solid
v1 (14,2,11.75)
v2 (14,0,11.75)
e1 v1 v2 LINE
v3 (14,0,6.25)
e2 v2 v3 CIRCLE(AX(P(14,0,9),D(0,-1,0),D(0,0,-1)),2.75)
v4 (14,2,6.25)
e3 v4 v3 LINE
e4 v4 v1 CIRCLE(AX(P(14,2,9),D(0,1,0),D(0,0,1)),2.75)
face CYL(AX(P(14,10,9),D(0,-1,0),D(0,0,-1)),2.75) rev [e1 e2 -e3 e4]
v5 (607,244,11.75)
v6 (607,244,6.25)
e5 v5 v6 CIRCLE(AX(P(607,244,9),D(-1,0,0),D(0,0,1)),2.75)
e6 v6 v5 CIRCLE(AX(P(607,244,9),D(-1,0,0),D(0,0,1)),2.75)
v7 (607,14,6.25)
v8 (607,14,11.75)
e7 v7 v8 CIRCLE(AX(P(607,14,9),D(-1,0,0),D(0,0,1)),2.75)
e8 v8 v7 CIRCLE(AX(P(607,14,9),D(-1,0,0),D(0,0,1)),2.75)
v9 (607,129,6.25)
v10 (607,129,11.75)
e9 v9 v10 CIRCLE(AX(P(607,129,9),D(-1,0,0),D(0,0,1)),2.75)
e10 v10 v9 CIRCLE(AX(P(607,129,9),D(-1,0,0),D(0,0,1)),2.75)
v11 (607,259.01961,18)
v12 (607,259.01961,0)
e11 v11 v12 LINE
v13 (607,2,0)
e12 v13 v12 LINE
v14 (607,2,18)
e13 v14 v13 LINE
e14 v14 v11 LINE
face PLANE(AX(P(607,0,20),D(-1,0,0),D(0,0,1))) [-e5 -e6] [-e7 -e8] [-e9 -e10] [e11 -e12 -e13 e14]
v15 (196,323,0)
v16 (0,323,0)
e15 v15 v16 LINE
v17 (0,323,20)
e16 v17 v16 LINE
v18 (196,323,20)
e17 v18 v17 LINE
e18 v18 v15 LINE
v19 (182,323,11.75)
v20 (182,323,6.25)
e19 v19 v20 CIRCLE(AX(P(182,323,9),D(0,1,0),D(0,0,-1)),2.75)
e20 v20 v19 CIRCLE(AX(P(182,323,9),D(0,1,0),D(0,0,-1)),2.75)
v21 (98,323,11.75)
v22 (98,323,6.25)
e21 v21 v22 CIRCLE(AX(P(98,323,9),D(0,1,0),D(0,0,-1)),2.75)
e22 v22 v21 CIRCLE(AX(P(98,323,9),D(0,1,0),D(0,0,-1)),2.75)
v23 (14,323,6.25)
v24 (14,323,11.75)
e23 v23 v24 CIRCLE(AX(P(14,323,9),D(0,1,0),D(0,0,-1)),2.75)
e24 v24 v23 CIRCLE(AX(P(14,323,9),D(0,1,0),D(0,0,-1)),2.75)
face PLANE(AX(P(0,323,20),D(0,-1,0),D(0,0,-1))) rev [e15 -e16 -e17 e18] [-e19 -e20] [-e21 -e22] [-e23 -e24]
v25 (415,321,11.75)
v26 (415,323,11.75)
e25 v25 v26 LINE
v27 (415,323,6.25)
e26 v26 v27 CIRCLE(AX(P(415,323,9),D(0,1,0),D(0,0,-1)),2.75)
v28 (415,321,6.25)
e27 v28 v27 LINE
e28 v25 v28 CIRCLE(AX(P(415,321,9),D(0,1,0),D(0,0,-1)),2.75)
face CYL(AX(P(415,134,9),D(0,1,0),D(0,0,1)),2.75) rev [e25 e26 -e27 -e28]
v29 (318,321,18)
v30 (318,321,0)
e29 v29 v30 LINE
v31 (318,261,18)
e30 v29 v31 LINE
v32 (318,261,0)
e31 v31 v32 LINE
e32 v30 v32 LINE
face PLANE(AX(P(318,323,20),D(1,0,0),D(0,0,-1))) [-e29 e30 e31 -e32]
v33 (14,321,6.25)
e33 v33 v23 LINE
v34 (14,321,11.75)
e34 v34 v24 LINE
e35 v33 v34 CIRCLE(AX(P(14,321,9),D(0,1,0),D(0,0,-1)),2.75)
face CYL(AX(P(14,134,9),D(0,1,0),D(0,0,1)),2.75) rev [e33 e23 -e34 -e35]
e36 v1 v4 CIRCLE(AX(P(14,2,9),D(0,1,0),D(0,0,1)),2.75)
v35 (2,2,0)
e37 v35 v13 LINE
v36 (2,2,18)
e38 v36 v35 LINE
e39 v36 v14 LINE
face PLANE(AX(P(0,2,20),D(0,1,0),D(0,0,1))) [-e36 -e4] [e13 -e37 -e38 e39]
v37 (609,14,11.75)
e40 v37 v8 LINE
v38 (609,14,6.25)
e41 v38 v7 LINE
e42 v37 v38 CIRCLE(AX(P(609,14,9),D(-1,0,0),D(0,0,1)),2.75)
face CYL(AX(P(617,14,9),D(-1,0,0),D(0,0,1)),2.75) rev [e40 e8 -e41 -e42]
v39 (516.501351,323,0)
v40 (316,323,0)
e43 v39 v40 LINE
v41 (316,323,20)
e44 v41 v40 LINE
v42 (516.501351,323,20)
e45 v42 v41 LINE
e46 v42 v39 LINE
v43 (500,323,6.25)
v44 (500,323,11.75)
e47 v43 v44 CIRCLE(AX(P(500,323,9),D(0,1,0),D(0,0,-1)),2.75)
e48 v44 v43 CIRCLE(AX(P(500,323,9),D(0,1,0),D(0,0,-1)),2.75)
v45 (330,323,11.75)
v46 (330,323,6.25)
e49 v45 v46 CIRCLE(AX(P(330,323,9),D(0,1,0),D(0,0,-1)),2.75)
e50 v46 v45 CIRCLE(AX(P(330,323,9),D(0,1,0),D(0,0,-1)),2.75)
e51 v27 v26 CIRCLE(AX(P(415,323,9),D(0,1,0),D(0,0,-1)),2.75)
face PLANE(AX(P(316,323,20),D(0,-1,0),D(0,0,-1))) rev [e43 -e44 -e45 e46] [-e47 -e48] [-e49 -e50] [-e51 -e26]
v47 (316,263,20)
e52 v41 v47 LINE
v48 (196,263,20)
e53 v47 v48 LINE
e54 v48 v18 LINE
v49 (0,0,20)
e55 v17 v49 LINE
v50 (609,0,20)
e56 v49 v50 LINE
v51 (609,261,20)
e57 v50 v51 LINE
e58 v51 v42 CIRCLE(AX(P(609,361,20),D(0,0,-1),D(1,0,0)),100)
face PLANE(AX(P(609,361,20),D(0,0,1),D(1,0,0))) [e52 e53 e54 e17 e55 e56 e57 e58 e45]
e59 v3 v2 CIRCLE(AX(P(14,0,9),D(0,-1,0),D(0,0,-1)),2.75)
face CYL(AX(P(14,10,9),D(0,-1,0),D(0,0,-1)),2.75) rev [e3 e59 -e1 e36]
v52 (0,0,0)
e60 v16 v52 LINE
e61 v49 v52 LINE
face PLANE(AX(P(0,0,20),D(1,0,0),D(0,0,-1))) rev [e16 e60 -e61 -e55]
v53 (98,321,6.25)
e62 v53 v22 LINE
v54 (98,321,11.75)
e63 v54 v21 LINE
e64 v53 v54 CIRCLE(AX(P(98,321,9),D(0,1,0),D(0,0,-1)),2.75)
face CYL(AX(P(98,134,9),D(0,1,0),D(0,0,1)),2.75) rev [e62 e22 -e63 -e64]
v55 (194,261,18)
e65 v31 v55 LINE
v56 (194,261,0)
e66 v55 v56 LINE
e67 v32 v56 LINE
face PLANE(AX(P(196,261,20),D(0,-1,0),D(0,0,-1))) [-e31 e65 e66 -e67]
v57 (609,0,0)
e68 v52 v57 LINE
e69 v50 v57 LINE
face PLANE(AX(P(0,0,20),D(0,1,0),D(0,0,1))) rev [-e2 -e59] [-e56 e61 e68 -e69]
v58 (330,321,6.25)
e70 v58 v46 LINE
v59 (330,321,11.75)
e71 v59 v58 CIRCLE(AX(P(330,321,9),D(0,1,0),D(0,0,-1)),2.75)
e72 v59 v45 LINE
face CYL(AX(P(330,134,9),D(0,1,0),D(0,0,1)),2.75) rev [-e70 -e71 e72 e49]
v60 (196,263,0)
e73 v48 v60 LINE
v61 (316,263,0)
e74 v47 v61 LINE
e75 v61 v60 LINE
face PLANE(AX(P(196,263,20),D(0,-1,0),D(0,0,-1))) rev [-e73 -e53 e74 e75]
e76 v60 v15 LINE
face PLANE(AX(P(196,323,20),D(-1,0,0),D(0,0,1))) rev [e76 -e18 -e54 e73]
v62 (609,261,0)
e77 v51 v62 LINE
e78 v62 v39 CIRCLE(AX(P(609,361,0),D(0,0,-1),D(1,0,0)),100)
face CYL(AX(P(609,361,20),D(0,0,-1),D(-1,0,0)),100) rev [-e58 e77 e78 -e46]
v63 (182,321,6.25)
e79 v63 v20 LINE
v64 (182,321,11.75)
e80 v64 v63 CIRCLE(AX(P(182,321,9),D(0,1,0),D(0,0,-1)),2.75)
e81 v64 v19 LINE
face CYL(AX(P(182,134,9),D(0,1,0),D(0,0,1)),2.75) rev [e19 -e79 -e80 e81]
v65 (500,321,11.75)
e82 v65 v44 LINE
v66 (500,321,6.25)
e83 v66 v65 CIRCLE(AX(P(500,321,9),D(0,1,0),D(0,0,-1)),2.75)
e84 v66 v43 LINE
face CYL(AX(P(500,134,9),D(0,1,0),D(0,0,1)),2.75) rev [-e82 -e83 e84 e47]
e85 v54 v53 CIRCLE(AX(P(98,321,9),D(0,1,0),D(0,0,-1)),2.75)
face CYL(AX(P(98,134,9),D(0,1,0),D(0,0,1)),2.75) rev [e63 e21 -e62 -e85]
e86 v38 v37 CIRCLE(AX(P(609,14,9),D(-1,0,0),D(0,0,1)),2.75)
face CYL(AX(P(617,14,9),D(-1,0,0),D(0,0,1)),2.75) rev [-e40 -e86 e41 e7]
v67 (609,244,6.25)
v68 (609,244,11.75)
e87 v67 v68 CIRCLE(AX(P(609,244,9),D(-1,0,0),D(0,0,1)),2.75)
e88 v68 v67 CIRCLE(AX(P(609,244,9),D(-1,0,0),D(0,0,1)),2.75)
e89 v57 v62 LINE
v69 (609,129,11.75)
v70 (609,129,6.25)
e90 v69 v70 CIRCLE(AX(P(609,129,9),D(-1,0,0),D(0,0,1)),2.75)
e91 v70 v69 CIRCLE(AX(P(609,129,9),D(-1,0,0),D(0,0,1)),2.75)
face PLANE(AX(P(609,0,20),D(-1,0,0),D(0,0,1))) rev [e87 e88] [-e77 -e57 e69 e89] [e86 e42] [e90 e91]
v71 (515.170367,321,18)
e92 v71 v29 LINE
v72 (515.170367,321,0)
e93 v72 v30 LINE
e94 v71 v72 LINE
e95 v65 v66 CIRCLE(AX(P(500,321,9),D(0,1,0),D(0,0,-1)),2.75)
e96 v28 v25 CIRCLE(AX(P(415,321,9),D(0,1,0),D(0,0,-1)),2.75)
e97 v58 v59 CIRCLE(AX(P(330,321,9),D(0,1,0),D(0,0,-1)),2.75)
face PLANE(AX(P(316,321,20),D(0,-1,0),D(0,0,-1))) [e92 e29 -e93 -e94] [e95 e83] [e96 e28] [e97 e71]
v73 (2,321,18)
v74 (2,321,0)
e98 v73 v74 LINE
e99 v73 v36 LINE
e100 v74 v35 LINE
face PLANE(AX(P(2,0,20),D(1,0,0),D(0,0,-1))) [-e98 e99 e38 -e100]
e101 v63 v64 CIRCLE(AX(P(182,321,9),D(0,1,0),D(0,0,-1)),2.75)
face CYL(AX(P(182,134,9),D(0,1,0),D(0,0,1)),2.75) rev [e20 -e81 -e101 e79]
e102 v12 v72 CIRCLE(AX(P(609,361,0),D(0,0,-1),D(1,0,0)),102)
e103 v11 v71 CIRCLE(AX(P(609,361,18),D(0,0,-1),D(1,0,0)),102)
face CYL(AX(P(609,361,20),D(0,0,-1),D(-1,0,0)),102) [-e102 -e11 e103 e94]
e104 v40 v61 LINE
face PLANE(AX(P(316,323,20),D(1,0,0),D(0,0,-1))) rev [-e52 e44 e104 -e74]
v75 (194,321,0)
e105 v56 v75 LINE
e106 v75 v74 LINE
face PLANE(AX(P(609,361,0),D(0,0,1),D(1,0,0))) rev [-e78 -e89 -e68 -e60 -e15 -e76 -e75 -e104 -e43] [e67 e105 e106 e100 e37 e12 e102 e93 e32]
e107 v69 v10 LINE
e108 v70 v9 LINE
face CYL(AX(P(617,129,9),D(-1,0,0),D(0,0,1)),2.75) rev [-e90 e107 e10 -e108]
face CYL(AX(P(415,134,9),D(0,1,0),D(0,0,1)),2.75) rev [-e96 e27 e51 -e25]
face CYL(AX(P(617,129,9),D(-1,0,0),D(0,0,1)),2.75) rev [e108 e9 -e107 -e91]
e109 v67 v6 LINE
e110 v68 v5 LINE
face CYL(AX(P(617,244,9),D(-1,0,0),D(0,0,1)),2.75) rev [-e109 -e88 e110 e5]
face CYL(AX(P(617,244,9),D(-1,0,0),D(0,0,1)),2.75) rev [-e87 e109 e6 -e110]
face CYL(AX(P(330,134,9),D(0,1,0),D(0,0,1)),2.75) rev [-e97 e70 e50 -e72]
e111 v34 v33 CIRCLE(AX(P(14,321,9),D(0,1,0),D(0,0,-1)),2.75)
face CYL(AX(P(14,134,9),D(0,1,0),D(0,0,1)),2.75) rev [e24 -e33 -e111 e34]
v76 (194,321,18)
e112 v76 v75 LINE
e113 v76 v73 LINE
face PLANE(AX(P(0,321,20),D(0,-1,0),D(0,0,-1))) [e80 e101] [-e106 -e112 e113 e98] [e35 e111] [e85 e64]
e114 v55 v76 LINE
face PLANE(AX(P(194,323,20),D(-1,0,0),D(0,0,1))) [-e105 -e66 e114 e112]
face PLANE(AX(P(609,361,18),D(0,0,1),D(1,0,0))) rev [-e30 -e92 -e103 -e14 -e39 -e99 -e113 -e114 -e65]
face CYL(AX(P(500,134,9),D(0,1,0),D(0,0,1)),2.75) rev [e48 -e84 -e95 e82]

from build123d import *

# Parameters (mm, degrees)
EXTRUDE_1_DEPTH          = 20
SHELL_1_T                = -2
CUT_EXTRUDE_1_DEPTH      = 187
CUT_EXTRUDE_1_DEPTH_BACK = 10
SKETCH_2_R               = 2.75
SKETCH_3_R               = 2.75
CUT_EXTRUDE_2_DEPTH      = 10
SKETCH_4_R               = 2.75
CUT_EXTRUDE_3_DEPTH      = 10


with BuildPart() as part:
    # 草图1 → 凸台-拉伸1 (new body)
    with BuildSketch(Plane.XY):
        with BuildLine():
            Line((0, 0), (609, 0))
            Line((609, 0), (609, 261))
            ThreePointArc((609, 261), (553.322356372, 277.933761371), (516.501351361, 323))
            Line((516.501351361, 323), (316, 323))
            Line((316, 323), (316, 263))
            Line((316, 263), (196, 263))
            Line((196, 263), (196, 323))
            Line((196, 323), (0, 323))
            Line((0, 323), (0, 0))
        make_face()
    extrude(amount=EXTRUDE_1_DEPTH)

    # 抽壳1
    shell_1_openings = [part.faces().sort_by_distance(p)[0] for p in [
        (300.393153284, 153.35137278, 0),
    ]]
    offset(amount=SHELL_1_T, openings=shell_1_openings, kind=Kind.INTERSECTION)

    # 草图2 → 切除-拉伸1 (cut, two sides: drawn at the far end of the back side and taken through both)
    with BuildSketch(Plane.XZ.offset(-321).offset(-CUT_EXTRUDE_1_DEPTH_BACK)):
        with Locations(Location((14, 9, 0), (0, 0, 270))):
            Circle(SKETCH_2_R)
        with Locations(Location((182, 9, 0), (0, 0, 270))):
            Circle(SKETCH_2_R)
        with Locations(Location((98, 9, 0), (0, 0, 270))):
            Circle(SKETCH_2_R)
        with Locations(Location((330, 9, 0), (0, 0, 270))):
            Circle(SKETCH_2_R)
        with Locations(Location((500, 9, 0), (0, 0, 270))):
            Circle(SKETCH_2_R)
        with Locations(Location((415, 9, 0), (0, 0, 270))):
            Circle(SKETCH_2_R)
    extrude(amount=CUT_EXTRUDE_1_DEPTH + CUT_EXTRUDE_1_DEPTH_BACK, mode=Mode.SUBTRACT)

    # 草图3 → 切除-拉伸2 (cut)
    with BuildSketch(Plane.XZ):
        with Locations(Location((14, 9, 0), (0, 0, 270))):
            Circle(SKETCH_3_R)
    extrude(amount=-CUT_EXTRUDE_2_DEPTH, mode=Mode.SUBTRACT)

    # 草图4 → 切除-拉伸3 (cut)
    with BuildSketch(Plane.ZY.offset(-607)):
        with Locations((9, 14)):
            Circle(SKETCH_4_R)
        with Locations((9, 129)):
            Circle(SKETCH_4_R)
        with Locations((9, 244)):
            Circle(SKETCH_4_R)
    extrude(amount=-CUT_EXTRUDE_3_DEPTH, mode=Mode.SUBTRACT)


solid = part.part
